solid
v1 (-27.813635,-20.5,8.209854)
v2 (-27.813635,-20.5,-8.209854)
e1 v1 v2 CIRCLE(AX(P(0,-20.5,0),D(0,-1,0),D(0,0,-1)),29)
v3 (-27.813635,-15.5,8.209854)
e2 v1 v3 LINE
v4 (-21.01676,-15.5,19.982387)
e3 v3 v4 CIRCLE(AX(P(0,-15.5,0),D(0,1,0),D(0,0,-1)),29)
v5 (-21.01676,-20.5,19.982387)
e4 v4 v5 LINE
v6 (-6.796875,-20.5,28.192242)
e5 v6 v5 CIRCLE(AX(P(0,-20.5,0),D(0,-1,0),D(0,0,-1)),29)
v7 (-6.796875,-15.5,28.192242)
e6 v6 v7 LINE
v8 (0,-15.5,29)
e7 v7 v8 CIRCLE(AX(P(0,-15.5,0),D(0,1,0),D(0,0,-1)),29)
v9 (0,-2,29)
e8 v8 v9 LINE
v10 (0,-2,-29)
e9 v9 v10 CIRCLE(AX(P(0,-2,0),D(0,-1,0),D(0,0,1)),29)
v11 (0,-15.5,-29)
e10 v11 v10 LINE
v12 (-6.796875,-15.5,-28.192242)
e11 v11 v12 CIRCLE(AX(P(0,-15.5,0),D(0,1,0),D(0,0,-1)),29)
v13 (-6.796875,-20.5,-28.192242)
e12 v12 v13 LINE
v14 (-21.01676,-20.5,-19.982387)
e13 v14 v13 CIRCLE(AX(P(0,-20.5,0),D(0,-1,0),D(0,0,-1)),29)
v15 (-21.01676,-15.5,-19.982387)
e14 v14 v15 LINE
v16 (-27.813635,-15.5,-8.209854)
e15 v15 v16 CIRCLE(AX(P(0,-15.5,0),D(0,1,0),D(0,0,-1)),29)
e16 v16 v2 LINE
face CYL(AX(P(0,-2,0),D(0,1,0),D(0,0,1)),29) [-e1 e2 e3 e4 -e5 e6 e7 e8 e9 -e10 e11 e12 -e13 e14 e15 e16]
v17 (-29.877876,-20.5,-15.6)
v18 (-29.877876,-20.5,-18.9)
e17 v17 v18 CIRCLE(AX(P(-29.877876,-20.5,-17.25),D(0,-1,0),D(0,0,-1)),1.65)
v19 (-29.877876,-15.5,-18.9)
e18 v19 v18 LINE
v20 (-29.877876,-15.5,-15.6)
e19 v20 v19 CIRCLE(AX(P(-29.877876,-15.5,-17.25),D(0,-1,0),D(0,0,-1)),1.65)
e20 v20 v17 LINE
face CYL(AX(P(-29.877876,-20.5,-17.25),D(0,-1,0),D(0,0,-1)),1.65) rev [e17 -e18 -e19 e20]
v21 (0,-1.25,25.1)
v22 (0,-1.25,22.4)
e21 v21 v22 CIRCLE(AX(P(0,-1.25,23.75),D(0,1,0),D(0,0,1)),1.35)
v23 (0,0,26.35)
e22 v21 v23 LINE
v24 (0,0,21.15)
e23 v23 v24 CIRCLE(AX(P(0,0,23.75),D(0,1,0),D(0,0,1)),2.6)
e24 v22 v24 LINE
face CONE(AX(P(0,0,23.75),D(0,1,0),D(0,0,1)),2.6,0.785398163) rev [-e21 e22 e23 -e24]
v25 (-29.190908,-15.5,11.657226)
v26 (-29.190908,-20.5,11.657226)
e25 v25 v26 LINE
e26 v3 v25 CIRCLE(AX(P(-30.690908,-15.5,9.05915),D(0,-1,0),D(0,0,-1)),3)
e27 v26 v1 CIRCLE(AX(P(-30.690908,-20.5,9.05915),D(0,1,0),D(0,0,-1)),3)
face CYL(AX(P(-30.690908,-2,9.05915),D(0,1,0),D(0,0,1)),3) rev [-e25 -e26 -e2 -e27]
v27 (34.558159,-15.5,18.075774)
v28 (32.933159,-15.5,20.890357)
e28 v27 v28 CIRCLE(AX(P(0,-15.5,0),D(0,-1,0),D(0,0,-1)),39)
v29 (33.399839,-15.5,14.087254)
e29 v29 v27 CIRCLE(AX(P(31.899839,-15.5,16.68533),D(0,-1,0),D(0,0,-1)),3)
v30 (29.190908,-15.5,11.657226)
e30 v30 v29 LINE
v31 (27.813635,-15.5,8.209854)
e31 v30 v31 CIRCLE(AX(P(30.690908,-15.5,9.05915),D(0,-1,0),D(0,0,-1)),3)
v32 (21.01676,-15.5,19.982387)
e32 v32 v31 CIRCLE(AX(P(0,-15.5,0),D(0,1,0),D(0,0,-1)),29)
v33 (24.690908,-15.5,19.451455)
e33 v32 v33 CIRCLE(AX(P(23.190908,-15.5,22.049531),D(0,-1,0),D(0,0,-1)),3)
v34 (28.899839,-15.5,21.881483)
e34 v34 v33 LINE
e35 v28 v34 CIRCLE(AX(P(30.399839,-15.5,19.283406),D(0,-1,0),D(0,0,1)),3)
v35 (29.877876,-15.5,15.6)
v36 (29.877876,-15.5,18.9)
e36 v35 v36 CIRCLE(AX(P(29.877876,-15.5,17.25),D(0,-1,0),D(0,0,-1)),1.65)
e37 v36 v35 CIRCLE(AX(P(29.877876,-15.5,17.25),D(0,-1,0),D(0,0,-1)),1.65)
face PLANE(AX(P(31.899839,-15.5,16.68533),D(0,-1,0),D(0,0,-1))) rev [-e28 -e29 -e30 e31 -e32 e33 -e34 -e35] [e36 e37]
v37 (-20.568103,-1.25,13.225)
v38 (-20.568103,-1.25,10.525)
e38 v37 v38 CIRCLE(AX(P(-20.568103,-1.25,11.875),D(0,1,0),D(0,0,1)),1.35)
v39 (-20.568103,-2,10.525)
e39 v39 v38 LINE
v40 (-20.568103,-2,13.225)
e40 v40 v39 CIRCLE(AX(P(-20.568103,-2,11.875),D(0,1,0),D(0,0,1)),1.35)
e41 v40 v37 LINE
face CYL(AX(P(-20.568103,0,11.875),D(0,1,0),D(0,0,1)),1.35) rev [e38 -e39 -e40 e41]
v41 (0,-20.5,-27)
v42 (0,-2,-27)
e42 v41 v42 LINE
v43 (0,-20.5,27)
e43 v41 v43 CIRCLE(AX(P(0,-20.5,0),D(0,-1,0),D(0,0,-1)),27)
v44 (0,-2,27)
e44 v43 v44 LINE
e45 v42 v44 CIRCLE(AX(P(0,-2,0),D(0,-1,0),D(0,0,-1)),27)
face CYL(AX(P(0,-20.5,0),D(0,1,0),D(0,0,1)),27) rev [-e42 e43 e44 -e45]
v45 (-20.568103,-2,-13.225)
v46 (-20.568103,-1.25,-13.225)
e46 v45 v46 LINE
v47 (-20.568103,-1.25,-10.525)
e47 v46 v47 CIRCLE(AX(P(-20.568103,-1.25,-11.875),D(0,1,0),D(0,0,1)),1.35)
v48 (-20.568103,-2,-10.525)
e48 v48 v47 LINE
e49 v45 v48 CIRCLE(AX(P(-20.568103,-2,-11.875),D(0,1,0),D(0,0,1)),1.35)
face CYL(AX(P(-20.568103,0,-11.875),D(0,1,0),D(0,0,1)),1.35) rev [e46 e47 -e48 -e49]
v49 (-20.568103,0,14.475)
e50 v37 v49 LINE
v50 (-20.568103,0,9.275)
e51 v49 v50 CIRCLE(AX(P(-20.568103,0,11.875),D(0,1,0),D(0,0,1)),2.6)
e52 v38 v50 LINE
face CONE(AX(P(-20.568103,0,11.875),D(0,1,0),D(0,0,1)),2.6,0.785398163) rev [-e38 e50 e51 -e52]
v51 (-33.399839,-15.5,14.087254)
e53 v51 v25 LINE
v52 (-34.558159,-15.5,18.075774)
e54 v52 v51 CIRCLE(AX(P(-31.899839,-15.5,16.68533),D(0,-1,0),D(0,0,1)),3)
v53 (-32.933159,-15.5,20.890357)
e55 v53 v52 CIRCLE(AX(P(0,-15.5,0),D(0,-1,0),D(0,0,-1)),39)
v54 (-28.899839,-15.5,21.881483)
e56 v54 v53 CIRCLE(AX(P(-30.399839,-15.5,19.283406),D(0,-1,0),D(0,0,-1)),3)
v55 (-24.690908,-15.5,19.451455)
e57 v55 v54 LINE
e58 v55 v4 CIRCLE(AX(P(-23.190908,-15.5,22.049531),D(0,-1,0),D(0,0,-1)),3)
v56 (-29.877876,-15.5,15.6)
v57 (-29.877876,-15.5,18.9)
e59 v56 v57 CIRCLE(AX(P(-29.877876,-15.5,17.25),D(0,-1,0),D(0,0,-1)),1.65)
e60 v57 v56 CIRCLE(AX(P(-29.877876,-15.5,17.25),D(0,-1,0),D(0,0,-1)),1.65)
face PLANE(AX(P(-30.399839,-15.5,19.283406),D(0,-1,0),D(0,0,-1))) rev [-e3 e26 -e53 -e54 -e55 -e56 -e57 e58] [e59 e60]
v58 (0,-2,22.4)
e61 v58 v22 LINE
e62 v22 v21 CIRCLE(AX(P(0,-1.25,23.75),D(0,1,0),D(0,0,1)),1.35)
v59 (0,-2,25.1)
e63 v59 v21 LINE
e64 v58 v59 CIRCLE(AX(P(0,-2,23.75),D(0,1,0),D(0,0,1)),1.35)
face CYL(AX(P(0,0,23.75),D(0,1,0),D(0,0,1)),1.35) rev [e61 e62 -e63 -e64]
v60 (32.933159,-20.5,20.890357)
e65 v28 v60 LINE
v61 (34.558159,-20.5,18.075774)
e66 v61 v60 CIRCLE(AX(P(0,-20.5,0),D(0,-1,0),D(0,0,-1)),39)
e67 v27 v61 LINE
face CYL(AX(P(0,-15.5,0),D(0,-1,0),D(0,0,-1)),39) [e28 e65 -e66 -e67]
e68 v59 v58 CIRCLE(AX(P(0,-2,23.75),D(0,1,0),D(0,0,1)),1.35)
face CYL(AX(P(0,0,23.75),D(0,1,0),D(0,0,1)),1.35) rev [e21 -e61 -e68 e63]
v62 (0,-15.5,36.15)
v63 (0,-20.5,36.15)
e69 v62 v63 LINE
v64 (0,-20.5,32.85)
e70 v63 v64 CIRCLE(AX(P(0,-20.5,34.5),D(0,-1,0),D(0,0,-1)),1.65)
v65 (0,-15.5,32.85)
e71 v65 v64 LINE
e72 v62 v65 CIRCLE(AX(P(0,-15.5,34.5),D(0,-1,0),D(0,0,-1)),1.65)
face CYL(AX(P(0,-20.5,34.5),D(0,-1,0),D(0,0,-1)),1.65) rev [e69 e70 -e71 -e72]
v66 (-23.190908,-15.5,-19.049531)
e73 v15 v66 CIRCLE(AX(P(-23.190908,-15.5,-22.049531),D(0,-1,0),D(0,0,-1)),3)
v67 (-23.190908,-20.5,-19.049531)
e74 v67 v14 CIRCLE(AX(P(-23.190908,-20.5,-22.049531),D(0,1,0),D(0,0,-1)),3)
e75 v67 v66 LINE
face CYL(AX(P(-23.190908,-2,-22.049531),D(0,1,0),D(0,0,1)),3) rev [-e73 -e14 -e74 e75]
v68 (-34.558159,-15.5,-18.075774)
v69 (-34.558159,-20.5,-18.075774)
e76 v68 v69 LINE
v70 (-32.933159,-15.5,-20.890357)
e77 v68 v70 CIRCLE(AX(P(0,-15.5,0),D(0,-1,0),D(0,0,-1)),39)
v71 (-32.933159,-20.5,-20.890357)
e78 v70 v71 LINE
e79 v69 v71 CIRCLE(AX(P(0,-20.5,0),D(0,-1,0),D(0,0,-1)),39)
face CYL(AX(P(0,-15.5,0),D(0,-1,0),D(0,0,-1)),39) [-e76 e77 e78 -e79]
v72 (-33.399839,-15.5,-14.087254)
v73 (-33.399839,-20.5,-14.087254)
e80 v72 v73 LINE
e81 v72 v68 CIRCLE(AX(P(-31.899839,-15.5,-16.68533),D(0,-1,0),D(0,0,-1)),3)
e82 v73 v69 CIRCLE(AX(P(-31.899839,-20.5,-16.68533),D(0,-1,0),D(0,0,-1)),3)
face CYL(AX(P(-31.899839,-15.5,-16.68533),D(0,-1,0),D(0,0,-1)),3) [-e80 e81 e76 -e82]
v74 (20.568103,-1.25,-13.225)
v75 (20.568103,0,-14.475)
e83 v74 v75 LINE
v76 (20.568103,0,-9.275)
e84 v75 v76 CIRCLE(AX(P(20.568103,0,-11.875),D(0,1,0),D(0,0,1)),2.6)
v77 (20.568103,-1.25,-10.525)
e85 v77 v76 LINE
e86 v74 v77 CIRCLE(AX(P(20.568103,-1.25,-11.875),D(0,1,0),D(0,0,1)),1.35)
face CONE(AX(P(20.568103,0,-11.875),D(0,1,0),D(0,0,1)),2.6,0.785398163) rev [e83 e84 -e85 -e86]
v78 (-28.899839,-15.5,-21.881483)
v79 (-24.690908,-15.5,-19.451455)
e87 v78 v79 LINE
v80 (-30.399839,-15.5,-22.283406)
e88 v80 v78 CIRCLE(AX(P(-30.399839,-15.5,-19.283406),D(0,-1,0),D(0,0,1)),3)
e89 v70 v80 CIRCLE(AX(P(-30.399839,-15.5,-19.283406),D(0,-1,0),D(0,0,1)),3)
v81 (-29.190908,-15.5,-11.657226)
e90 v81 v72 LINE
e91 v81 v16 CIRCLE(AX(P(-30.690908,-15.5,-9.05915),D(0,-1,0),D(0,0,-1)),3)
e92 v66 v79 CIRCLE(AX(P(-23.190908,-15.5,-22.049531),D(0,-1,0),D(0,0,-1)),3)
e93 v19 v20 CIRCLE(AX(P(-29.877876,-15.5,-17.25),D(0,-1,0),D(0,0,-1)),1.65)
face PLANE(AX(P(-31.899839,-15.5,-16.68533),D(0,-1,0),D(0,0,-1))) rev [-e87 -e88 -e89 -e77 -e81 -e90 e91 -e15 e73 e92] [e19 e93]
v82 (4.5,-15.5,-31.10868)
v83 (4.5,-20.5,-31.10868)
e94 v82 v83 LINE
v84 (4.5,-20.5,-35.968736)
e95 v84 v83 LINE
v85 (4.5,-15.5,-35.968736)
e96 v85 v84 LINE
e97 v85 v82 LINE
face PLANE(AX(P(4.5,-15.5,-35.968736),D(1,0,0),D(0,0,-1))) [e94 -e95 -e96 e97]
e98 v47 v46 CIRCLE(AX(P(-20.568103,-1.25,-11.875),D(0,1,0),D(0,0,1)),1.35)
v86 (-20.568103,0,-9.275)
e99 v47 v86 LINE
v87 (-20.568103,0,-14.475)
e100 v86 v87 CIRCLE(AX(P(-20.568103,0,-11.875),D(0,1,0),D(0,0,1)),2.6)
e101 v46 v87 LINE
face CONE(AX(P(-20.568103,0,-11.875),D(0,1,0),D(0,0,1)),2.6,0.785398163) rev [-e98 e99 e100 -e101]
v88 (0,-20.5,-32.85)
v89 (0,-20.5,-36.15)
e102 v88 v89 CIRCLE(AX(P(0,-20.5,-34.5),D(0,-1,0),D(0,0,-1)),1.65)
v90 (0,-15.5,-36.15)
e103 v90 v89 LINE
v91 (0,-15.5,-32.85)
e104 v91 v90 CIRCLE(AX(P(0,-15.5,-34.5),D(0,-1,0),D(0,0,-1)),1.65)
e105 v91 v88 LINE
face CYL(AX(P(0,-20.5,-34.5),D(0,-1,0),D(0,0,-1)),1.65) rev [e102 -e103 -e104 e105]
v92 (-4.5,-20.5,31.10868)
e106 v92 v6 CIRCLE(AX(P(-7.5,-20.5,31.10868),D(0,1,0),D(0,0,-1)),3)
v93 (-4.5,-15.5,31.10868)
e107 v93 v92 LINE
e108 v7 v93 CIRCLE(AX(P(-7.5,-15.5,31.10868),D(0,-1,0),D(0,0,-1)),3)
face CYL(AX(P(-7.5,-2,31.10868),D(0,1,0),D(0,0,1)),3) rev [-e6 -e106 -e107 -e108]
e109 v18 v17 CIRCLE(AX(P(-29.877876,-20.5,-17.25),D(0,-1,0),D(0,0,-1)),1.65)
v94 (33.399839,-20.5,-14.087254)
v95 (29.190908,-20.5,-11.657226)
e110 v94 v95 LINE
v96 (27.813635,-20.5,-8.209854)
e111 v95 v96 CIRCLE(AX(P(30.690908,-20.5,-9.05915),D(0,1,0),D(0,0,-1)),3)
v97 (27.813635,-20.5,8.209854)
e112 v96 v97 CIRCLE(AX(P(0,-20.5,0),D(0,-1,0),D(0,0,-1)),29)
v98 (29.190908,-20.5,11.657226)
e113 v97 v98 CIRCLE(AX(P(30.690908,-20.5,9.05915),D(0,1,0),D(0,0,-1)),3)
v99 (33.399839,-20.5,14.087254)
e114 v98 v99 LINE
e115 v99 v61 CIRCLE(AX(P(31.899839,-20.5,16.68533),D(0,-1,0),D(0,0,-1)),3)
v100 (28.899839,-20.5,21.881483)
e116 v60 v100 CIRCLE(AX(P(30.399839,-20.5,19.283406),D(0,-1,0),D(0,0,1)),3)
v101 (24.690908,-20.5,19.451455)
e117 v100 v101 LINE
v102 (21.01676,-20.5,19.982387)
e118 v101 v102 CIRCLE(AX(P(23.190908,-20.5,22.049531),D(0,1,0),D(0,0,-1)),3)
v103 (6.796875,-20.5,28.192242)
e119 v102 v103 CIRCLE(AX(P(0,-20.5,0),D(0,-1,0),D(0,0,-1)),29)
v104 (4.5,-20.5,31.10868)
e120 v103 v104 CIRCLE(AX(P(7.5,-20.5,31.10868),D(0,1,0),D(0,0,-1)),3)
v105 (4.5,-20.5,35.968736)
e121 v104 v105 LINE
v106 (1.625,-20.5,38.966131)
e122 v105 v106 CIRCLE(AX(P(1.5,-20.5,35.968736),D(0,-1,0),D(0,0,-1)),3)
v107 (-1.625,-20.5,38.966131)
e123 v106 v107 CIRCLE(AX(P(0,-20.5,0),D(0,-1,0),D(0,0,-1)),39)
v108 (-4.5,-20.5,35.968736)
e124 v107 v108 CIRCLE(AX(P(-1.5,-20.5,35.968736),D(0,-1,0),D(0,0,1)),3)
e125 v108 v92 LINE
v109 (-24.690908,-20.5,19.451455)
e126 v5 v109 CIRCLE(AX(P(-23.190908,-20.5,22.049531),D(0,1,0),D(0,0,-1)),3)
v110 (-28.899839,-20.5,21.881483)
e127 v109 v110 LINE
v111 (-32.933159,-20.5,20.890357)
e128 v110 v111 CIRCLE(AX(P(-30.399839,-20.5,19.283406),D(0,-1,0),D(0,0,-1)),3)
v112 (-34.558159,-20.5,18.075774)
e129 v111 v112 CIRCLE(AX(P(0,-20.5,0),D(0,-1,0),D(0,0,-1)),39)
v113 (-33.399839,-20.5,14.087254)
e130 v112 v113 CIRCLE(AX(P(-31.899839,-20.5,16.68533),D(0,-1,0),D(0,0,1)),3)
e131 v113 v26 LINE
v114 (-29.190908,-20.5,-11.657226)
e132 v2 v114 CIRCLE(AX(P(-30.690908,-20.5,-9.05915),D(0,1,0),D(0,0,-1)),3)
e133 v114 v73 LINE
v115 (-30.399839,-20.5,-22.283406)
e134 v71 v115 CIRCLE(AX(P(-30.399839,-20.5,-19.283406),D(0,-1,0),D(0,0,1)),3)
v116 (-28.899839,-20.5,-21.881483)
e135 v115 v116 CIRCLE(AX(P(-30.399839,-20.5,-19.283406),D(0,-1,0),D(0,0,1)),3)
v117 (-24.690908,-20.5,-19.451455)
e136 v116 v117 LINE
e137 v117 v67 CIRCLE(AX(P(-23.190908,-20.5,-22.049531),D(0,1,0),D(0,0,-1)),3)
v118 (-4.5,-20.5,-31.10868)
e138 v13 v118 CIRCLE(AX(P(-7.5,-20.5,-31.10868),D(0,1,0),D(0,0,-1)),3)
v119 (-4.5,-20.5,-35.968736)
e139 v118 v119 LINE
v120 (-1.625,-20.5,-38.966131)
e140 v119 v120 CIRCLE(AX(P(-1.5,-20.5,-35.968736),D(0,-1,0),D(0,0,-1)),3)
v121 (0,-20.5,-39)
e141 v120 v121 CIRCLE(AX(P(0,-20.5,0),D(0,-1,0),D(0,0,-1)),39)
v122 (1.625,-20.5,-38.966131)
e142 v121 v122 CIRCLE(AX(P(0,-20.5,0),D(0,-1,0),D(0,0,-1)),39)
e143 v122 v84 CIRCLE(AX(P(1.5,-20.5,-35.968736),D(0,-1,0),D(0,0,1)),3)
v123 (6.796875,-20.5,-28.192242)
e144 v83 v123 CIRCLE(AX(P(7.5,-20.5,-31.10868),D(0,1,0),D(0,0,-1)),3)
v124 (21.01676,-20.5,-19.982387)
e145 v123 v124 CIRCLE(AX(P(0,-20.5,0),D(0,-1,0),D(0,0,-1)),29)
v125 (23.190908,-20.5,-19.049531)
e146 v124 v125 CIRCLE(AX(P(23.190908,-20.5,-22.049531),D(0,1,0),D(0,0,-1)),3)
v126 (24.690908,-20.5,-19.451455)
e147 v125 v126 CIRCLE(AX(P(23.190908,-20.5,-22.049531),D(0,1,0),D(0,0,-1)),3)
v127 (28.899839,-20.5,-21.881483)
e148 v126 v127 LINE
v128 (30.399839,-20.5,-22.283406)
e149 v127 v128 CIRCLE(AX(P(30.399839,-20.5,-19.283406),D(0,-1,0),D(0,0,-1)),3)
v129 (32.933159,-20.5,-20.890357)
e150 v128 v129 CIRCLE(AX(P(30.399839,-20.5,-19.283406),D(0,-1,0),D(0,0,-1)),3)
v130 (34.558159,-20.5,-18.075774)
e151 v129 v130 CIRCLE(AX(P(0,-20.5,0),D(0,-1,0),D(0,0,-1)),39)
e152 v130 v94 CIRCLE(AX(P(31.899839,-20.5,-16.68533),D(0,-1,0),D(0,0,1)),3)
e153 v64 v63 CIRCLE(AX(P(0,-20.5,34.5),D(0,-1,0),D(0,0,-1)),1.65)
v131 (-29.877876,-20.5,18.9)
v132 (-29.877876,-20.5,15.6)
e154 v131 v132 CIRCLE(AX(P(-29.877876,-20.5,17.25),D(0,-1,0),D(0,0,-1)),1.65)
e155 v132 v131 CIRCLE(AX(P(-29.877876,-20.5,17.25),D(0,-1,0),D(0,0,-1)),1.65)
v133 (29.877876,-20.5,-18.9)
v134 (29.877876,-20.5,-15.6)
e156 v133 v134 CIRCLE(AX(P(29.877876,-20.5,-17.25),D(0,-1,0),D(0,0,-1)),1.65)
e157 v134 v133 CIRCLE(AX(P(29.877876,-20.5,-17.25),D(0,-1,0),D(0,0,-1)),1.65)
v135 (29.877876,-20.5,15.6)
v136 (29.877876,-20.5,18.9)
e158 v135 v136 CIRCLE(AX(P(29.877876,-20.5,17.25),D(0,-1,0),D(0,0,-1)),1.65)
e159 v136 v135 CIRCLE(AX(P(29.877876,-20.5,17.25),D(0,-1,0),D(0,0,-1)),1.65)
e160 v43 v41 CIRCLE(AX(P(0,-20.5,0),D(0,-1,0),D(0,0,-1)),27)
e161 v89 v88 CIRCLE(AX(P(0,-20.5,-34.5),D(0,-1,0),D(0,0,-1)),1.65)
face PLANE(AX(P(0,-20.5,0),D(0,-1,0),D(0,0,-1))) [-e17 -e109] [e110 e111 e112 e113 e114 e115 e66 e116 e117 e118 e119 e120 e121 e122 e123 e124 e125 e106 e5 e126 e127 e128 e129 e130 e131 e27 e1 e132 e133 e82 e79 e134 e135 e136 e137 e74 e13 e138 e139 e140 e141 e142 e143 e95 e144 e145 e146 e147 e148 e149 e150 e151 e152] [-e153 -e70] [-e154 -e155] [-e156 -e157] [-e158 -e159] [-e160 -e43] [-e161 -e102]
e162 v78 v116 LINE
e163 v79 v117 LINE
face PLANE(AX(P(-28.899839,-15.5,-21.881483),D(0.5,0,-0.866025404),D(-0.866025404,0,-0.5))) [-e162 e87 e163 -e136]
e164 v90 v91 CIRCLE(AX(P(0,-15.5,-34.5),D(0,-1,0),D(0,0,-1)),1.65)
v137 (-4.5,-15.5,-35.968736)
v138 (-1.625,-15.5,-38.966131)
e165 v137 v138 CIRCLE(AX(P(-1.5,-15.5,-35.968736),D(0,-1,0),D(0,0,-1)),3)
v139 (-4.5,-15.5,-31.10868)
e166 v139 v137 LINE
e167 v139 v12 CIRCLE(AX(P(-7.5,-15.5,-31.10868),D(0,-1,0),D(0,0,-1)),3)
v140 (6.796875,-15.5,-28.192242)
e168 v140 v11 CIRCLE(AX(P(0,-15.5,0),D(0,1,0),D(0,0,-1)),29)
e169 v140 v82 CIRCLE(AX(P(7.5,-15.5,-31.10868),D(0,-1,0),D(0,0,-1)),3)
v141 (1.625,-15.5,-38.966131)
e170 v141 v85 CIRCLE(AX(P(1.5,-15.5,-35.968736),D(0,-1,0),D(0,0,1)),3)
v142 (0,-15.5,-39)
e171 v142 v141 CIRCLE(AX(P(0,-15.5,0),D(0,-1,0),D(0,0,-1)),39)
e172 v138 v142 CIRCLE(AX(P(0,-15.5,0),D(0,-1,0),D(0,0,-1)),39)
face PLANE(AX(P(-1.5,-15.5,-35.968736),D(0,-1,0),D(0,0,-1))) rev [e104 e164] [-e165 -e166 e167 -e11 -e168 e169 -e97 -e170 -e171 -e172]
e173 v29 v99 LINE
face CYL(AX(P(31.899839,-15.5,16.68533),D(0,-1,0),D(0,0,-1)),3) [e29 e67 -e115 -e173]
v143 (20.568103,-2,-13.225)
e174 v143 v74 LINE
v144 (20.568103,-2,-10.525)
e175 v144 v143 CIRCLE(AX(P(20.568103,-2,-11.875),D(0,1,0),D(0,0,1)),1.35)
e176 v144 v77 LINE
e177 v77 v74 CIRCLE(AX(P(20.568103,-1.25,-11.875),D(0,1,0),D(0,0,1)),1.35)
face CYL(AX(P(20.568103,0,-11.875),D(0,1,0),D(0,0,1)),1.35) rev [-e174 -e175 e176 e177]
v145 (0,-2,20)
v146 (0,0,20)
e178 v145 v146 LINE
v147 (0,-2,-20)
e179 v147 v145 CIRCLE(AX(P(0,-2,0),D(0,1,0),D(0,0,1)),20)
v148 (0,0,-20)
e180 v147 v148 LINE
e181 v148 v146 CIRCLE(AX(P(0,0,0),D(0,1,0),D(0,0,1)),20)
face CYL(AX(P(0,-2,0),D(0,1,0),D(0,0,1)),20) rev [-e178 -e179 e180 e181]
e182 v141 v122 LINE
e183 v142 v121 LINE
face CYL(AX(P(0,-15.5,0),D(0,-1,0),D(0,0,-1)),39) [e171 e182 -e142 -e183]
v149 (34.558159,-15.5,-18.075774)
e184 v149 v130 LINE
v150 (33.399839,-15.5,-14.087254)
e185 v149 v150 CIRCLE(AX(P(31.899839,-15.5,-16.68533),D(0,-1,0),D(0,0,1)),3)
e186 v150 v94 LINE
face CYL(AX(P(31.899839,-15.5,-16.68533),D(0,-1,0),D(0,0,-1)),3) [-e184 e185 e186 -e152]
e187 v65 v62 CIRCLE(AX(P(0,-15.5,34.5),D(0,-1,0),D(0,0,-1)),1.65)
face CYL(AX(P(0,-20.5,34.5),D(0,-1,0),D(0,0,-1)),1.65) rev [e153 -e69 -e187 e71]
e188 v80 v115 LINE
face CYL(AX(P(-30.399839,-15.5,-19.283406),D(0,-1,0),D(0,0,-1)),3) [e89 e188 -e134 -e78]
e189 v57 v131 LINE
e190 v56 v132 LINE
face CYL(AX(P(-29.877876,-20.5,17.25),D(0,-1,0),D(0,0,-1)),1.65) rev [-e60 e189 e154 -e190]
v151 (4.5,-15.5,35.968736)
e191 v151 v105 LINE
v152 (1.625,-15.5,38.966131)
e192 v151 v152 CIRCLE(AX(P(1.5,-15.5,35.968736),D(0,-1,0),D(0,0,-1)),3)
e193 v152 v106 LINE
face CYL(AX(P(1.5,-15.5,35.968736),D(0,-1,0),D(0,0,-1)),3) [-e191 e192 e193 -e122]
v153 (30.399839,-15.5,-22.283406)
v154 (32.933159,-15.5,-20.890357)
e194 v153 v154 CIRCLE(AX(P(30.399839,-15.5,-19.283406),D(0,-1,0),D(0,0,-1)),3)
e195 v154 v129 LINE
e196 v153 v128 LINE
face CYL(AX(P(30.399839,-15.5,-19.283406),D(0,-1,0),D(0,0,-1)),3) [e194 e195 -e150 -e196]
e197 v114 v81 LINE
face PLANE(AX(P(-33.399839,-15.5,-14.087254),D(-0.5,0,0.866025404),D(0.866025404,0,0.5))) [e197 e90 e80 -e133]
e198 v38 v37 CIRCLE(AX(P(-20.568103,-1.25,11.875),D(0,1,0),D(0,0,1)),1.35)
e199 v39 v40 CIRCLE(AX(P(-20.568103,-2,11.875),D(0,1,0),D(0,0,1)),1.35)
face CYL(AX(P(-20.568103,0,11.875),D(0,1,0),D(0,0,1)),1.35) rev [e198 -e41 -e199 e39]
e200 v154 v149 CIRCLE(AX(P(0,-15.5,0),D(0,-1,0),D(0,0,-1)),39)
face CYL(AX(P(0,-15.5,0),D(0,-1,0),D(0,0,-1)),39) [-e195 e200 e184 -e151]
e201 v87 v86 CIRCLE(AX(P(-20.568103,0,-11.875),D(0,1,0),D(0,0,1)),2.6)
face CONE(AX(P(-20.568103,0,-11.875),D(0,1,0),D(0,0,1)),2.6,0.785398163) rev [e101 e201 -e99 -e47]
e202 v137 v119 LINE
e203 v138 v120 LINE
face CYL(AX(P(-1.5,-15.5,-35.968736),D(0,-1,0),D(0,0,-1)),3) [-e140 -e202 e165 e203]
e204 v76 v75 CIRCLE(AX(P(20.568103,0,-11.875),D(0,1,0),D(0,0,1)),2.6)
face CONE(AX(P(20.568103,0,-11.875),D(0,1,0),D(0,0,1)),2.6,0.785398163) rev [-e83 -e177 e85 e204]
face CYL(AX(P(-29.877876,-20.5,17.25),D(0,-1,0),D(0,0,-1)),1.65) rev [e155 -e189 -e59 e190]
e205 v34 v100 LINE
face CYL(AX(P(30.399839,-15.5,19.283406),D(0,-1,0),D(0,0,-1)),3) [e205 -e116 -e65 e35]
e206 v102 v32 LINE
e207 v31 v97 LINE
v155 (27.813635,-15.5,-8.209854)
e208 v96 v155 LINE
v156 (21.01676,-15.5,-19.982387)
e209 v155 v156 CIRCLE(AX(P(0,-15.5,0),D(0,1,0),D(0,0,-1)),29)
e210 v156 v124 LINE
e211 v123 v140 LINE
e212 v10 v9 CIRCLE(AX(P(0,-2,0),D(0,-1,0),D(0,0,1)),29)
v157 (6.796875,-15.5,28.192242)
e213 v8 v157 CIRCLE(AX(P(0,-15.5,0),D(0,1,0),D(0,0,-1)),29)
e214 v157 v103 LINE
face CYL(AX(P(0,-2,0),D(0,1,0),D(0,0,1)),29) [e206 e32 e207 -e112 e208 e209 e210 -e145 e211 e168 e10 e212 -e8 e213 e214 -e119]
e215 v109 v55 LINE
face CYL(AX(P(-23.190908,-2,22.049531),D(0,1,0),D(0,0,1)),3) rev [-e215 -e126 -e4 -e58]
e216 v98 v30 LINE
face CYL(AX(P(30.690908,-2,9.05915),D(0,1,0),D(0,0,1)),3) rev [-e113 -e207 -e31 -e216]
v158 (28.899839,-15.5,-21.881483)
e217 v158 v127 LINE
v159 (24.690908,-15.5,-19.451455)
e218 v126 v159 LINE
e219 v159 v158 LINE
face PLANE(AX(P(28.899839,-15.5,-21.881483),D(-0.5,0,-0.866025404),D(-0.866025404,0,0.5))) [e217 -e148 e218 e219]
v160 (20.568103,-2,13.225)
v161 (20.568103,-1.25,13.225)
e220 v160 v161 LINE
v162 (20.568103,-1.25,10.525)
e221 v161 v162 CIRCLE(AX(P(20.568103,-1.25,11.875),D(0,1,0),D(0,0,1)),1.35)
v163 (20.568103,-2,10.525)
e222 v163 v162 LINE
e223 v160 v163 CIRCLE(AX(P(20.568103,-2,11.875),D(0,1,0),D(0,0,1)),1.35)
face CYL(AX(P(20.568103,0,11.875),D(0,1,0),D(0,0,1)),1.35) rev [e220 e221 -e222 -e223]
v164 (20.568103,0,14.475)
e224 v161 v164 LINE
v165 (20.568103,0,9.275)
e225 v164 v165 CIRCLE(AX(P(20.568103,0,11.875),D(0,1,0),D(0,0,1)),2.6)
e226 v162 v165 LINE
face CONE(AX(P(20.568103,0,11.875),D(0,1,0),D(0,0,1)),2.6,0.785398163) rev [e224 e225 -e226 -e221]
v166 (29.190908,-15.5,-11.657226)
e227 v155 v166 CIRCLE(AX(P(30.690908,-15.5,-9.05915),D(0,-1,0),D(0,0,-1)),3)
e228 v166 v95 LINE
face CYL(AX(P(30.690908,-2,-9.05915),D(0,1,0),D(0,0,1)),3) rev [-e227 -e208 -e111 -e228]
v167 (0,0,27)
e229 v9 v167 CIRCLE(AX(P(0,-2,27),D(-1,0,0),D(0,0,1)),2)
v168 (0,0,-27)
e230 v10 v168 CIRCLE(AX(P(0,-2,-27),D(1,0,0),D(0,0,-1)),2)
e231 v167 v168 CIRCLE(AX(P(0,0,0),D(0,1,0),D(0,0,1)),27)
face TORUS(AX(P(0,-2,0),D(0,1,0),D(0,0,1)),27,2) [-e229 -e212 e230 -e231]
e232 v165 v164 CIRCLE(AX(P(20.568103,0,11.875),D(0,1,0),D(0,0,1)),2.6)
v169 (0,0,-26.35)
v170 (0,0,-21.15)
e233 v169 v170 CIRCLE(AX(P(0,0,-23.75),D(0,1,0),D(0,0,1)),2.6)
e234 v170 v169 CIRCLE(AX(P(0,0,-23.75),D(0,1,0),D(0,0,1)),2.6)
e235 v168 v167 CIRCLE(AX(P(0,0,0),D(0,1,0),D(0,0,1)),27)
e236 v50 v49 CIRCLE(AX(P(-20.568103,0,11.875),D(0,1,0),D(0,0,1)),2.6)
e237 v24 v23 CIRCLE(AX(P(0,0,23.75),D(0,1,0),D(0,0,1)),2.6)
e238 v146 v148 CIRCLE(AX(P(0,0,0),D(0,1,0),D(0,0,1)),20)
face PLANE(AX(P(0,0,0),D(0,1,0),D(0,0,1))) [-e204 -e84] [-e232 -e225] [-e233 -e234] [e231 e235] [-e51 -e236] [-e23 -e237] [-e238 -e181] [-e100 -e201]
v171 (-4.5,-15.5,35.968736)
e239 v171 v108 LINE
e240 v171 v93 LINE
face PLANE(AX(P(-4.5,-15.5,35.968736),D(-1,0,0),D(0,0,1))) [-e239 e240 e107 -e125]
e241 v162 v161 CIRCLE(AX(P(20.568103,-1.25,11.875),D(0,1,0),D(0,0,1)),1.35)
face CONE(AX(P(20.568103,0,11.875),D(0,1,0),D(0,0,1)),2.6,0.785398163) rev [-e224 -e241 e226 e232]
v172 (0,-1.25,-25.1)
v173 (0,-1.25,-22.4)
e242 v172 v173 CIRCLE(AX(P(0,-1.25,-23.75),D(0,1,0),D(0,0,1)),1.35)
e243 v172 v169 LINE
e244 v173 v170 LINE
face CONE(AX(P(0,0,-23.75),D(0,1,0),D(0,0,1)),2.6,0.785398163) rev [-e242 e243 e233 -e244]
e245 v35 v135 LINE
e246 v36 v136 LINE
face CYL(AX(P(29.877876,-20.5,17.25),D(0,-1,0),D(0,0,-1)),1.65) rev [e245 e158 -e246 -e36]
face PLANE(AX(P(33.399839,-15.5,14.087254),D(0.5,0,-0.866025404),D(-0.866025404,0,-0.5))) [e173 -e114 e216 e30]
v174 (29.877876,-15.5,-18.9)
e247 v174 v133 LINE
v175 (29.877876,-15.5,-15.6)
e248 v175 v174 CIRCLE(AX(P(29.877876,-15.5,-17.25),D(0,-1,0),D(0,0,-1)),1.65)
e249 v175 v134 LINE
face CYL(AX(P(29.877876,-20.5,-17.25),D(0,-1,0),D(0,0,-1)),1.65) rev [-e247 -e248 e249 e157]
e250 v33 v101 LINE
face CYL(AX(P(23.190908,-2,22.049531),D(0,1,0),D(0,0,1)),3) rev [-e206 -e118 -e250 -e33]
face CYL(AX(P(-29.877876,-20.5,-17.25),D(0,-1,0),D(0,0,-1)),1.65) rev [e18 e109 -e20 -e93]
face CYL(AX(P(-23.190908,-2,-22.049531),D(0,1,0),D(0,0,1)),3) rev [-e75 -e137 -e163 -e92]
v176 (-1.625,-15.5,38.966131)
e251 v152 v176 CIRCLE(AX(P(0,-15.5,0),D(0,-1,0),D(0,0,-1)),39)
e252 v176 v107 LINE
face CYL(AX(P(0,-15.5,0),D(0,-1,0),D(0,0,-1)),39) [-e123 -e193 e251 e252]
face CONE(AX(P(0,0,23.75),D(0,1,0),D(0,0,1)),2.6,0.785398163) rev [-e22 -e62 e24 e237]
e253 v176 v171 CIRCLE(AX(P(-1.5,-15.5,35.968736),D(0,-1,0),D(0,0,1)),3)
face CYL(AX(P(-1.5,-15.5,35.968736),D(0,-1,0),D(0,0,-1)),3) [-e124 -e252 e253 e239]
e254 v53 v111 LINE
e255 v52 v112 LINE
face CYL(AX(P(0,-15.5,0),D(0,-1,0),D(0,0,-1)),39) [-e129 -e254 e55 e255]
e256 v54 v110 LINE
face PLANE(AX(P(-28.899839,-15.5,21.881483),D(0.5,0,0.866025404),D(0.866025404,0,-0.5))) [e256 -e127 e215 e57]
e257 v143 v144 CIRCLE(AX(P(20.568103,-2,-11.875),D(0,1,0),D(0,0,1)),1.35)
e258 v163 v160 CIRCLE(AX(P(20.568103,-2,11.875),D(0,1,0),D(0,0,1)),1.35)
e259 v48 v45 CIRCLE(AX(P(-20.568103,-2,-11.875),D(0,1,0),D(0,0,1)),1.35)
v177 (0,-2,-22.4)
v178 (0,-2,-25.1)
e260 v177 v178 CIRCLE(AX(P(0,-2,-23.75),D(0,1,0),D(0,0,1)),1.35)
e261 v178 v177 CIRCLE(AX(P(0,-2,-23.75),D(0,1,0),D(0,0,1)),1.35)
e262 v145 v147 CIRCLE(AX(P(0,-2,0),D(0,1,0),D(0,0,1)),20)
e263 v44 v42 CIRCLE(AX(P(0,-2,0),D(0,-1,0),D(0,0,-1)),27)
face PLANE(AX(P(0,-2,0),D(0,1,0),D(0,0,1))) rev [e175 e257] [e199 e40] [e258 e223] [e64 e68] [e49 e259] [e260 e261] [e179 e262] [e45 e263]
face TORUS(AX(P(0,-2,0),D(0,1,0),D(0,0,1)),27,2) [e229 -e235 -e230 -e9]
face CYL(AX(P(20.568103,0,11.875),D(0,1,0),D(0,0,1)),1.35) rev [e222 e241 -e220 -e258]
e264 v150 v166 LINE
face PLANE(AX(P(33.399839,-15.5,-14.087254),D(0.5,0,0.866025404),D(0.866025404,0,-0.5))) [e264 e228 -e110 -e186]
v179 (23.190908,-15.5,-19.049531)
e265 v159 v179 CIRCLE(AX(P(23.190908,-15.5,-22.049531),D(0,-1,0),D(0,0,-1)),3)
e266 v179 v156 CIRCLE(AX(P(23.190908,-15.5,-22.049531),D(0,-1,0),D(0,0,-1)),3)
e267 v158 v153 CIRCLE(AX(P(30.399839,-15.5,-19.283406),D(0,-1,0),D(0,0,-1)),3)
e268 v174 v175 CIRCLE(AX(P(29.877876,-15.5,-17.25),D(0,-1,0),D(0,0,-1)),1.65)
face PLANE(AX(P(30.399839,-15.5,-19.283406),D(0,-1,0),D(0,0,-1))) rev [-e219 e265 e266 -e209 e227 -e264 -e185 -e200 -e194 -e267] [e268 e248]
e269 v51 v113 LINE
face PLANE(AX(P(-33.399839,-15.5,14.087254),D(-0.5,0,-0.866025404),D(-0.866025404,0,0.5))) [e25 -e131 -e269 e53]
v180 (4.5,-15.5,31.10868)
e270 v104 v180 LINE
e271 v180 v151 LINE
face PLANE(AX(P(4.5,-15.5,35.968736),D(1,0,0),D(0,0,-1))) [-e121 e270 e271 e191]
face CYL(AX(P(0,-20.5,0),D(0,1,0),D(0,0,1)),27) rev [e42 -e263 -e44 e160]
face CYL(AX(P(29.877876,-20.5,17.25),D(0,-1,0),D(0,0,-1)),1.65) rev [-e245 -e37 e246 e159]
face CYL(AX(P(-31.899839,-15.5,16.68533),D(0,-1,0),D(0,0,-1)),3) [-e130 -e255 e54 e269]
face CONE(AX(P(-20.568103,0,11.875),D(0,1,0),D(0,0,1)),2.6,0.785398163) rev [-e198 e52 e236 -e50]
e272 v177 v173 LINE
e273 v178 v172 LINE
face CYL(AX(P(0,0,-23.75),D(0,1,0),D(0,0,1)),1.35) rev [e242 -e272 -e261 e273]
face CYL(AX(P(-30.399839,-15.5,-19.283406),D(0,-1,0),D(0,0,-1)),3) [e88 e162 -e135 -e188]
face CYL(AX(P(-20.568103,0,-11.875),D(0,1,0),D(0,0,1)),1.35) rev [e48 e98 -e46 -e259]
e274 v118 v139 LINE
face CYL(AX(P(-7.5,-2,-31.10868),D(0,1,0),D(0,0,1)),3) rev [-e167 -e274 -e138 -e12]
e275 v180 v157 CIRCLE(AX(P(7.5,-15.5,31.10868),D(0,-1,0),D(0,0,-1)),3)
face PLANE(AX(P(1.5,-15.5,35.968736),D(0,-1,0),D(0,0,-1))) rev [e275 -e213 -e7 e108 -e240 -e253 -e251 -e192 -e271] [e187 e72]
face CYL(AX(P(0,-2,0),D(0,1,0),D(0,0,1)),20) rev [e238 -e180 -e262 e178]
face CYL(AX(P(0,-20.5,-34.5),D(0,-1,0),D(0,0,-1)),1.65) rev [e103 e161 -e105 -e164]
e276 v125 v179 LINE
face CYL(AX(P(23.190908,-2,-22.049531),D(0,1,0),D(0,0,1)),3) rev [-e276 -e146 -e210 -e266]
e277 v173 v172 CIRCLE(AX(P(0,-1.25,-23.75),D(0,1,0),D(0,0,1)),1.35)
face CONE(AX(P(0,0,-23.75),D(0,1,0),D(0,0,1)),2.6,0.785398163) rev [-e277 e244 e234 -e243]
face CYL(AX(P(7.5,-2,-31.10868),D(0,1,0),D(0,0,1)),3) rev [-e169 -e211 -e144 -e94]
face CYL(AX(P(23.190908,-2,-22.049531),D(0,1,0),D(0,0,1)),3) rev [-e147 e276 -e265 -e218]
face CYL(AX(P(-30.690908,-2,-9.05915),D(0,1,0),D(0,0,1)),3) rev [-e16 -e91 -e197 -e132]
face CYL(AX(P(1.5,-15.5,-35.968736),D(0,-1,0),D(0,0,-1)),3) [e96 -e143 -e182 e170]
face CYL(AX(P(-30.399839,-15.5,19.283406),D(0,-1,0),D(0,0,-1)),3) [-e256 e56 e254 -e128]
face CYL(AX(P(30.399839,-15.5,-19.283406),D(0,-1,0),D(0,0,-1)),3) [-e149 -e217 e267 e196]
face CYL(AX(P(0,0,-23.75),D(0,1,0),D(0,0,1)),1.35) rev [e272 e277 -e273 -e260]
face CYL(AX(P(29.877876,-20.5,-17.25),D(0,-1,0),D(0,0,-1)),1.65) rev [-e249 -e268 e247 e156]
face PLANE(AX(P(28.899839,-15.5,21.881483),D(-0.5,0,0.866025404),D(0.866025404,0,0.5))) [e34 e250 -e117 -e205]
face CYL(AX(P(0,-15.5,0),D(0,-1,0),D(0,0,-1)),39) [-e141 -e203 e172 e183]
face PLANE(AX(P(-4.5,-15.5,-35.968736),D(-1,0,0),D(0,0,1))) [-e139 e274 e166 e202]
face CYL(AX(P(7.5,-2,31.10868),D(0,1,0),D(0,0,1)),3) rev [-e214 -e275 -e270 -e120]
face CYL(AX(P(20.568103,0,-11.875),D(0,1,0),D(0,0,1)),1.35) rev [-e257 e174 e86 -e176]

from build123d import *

# Parameters (mm, degrees)
SKETCH_1_R                   = 29
SKETCH_1_R_2                 = 20
SKETCH_1_R_3                 = 1.3
EXTRUDE_1_DEPTH              = 2
SKETCH_2_R                   = 29
SKETCH_2_R_2                 = 27
EXTRUDE_2_DEPTH              = 18.5
EXTRUDE_START                = -5
EXTRUDE_3_DEPTH              = 5
HOLE_WIZARD_M4_1_D           = 3.3
FILLET_1_R                   = 3
FILLET_2_R                   = 2
HOLE_WIZARD_M3_1_D           = 2.7
HOLE_WIZARD_M3_1_CSINK_D     = 5.2
HOLE_WIZARD_M3_1_CSINK_ANGLE = 90


with BuildPart() as part:
    # 草图1 → 凸台-拉伸1 (new body)
    with BuildSketch(Plane(origin=(0, 0, 0), x_dir=(1, 0, 0), z_dir=(0, 1, 0))):
        with Locations(Location((0, 0, 0), (0, 0, 270))):
            Circle(SKETCH_1_R)
        with Locations(Location((0, 0, 0), (0, 0, 270))):
            Circle(SKETCH_1_R_2, mode=Mode.SUBTRACT)
        with Locations(Location((0, 23.75, 0), (0, 0, 270))):
            Circle(SKETCH_1_R_3, mode=Mode.SUBTRACT)
        with Locations(Location((20.56810334, 11.875, 0), (0, 0, 270))):
            Circle(SKETCH_1_R_3, mode=Mode.SUBTRACT)
        with Locations(Location((20.56810334, -11.875, 0), (0, 0, 270))):
            Circle(SKETCH_1_R_3, mode=Mode.SUBTRACT)
        with Locations(Location((0, -23.75, 0), (0, 0, 270))):
            Circle(SKETCH_1_R_3, mode=Mode.SUBTRACT)
        with Locations(Location((-20.56810334, -11.875, 0), (0, 0, 270))):
            Circle(SKETCH_1_R_3, mode=Mode.SUBTRACT)
        with Locations(Location((-20.56810334, 11.875, 0), (0, 0, 270))):
            Circle(SKETCH_1_R_3, mode=Mode.SUBTRACT)
    extrude(amount=-EXTRUDE_1_DEPTH)

    # 草图2 → 凸台-拉伸2 (add)
    with BuildSketch(Plane.XZ.offset(2)):
        with Locations(Location((0, 0, 0), (0, 0, 90))):
            Circle(SKETCH_2_R)
        with Locations(Location((0, 0, 0), (0, 0, 270))):
            Circle(SKETCH_2_R_2, mode=Mode.SUBTRACT)
    extrude(amount=EXTRUDE_2_DEPTH)

    # 草图3 → 凸台-拉伸3 (add)
    with BuildSketch(Plane.XZ.offset(20.5).offset(EXTRUDE_START)):
        with BuildLine():
            Line((-4.5, 35.968736425), (-4.5, 28.648734702))
            ThreePointArc((-4.5, 28.648734702), (0, 29), (4.5, 28.648734702))
            Line((4.5, 28.648734702), (4.5, 35.968736425))
            ThreePointArc((4.5, 35.968736425), (3.665063509, 38.045392391), (1.625, 38.966131127))
            ThreePointArc((1.625, 38.966131127), (0, 39), (-1.625, 38.966131127))
            ThreePointArc((-1.625, 38.966131127), (-3.665063509, 38.045392391), (-4.5, 35.968736425))
        make_face()
        with BuildLine():
            Line((28.899839486, 21.881482529), (22.560532038, 18.221481668))
            ThreePointArc((22.560532038, 18.221481668), (25.11473671, 14.5), (27.060532038, 10.427253034))
            Line((27.060532038, 10.427253034), (33.399839486, 14.087253895))
            ThreePointArc((33.399839486, 14.087253895), (34.780808062, 15.84865809), (34.558159443, 18.075774282))
            ThreePointArc((34.558159443, 18.075774282), (33.774990748, 19.5), (32.933159443, 20.890356845))
            ThreePointArc((32.933159443, 20.890356845), (31.115744552, 22.196734301), (28.899839486, 21.881482529))
        make_face()
        with BuildLine():
            Line((33.399839486, -14.087253895), (27.060532038, -10.427253034))
            ThreePointArc((27.060532038, -10.427253034), (25.11473671, -14.5), (22.560532038, -18.221481668))
            Line((22.560532038, -18.221481668), (28.899839486, -21.881482529))
            ThreePointArc((28.899839486, -21.881482529), (31.115744552, -22.196734301), (32.933159443, -20.890356845))
            ThreePointArc((32.933159443, -20.890356845), (33.774990748, -19.5), (34.558159443, -18.075774282))
            ThreePointArc((34.558159443, -18.075774282), (34.780808062, -15.84865809), (33.399839486, -14.087253895))
        make_face()
        with BuildLine():
            Line((4.5, -35.968736425), (4.5, -28.648734702))
            ThreePointArc((4.5, -28.648734702), (0, -29), (-4.5, -28.648734702))
            Line((-4.5, -28.648734702), (-4.5, -35.968736425))
            ThreePointArc((-4.5, -35.968736425), (-3.665063509, -38.045392391), (-1.625, -38.966131127))
            ThreePointArc((-1.625, -38.966131127), (0, -39), (1.625, -38.966131127))
            ThreePointArc((1.625, -38.966131127), (3.665063509, -38.045392391), (4.5, -35.968736425))
        make_face()
        with BuildLine():
            Line((-28.899839486, -21.881482529), (-22.560532038, -18.221481668))
            ThreePointArc((-22.560532038, -18.221481668), (-25.11473671, -14.5), (-27.060532038, -10.427253034))
            Line((-27.060532038, -10.427253034), (-33.399839486, -14.087253895))
            ThreePointArc((-33.399839486, -14.087253895), (-34.780808062, -15.84865809), (-34.558159443, -18.075774282))
            ThreePointArc((-34.558159443, -18.075774282), (-33.774990748, -19.5), (-32.933159443, -20.890356845))
            ThreePointArc((-32.933159443, -20.890356845), (-31.115744552, -22.196734301), (-28.899839486, -21.881482529))
        make_face()
        with BuildLine():
            Line((-33.399839486, 14.087253895), (-27.060532038, 10.427253034))
            ThreePointArc((-27.060532038, 10.427253034), (-25.11473671, 14.5), (-22.560532038, 18.221481668))
            Line((-22.560532038, 18.221481668), (-28.899839486, 21.881482529))
            ThreePointArc((-28.899839486, 21.881482529), (-31.115744552, 22.196734301), (-32.933159443, 20.890356845))
            ThreePointArc((-32.933159443, 20.890356845), (-33.774990748, 19.5), (-34.558159443, 18.075774282))
            ThreePointArc((-34.558159443, 18.075774282), (-34.780808062, 15.84865809), (-33.399839486, 14.087253895))
        make_face()
    extrude(amount=EXTRUDE_3_DEPTH)

    # M4 螺纹孔1 (through all)
    with Locations(Plane.XZ.offset(20.5)):
        with Locations((-29.877876431, 17.25), (-29.877876431, -17.25), (0, -34.5), (29.877876431, -17.25), (29.877876431, 17.25), (0, 34.5)):
            Hole(HOLE_WIZARD_M4_1_D / 2)

    # 圆角1
    fillet_1_edges = [part.edges().sort_by_distance(p)[0] for p in [
        (-27.060532038, -18, -10.427253034),
        (-22.560532038, -18, -18.221481668),
        (-22.560532038, -18, 18.221481668),
        (-27.060532038, -18, 10.427253034),
        (4.5, -18, 28.648734702),
        (-4.5, -18, 28.648734702),
        (27.060532038, -18, 10.427253034),
        (22.560532038, -18, 18.221481668),
        (22.560532038, -18, -18.221481668),
        (27.060532038, -18, -10.427253034),
        (-4.5, -18, -28.648734702),
        (4.5, -18, -28.648734702),
    ]]
    fillet(fillet_1_edges, radius=FILLET_1_R)

    # 圆角2
    fillet_2_edges = [part.edges().sort_by_distance(p)[0] for p in [
        (0, 0, -29),
    ]]
    fillet(fillet_2_edges, radius=FILLET_2_R)

    # M3 内六角花形沉头螺钉的锥形沉头孔1 (through all)
    with Locations(Plane(origin=(0, 0, 0), x_dir=(1, 0, 0), z_dir=(0, 1, 0))):
        with Locations((0, 23.75), (20.56810334, 11.875), (20.56810334, -11.875), (0, -23.75), (-20.56810334, -11.875), (-20.56810334, 11.875)):
            CounterSinkHole(HOLE_WIZARD_M3_1_D / 2, HOLE_WIZARD_M3_1_CSINK_D / 2, counter_sink_angle=HOLE_WIZARD_M3_1_CSINK_ANGLE)


solid = part.part
